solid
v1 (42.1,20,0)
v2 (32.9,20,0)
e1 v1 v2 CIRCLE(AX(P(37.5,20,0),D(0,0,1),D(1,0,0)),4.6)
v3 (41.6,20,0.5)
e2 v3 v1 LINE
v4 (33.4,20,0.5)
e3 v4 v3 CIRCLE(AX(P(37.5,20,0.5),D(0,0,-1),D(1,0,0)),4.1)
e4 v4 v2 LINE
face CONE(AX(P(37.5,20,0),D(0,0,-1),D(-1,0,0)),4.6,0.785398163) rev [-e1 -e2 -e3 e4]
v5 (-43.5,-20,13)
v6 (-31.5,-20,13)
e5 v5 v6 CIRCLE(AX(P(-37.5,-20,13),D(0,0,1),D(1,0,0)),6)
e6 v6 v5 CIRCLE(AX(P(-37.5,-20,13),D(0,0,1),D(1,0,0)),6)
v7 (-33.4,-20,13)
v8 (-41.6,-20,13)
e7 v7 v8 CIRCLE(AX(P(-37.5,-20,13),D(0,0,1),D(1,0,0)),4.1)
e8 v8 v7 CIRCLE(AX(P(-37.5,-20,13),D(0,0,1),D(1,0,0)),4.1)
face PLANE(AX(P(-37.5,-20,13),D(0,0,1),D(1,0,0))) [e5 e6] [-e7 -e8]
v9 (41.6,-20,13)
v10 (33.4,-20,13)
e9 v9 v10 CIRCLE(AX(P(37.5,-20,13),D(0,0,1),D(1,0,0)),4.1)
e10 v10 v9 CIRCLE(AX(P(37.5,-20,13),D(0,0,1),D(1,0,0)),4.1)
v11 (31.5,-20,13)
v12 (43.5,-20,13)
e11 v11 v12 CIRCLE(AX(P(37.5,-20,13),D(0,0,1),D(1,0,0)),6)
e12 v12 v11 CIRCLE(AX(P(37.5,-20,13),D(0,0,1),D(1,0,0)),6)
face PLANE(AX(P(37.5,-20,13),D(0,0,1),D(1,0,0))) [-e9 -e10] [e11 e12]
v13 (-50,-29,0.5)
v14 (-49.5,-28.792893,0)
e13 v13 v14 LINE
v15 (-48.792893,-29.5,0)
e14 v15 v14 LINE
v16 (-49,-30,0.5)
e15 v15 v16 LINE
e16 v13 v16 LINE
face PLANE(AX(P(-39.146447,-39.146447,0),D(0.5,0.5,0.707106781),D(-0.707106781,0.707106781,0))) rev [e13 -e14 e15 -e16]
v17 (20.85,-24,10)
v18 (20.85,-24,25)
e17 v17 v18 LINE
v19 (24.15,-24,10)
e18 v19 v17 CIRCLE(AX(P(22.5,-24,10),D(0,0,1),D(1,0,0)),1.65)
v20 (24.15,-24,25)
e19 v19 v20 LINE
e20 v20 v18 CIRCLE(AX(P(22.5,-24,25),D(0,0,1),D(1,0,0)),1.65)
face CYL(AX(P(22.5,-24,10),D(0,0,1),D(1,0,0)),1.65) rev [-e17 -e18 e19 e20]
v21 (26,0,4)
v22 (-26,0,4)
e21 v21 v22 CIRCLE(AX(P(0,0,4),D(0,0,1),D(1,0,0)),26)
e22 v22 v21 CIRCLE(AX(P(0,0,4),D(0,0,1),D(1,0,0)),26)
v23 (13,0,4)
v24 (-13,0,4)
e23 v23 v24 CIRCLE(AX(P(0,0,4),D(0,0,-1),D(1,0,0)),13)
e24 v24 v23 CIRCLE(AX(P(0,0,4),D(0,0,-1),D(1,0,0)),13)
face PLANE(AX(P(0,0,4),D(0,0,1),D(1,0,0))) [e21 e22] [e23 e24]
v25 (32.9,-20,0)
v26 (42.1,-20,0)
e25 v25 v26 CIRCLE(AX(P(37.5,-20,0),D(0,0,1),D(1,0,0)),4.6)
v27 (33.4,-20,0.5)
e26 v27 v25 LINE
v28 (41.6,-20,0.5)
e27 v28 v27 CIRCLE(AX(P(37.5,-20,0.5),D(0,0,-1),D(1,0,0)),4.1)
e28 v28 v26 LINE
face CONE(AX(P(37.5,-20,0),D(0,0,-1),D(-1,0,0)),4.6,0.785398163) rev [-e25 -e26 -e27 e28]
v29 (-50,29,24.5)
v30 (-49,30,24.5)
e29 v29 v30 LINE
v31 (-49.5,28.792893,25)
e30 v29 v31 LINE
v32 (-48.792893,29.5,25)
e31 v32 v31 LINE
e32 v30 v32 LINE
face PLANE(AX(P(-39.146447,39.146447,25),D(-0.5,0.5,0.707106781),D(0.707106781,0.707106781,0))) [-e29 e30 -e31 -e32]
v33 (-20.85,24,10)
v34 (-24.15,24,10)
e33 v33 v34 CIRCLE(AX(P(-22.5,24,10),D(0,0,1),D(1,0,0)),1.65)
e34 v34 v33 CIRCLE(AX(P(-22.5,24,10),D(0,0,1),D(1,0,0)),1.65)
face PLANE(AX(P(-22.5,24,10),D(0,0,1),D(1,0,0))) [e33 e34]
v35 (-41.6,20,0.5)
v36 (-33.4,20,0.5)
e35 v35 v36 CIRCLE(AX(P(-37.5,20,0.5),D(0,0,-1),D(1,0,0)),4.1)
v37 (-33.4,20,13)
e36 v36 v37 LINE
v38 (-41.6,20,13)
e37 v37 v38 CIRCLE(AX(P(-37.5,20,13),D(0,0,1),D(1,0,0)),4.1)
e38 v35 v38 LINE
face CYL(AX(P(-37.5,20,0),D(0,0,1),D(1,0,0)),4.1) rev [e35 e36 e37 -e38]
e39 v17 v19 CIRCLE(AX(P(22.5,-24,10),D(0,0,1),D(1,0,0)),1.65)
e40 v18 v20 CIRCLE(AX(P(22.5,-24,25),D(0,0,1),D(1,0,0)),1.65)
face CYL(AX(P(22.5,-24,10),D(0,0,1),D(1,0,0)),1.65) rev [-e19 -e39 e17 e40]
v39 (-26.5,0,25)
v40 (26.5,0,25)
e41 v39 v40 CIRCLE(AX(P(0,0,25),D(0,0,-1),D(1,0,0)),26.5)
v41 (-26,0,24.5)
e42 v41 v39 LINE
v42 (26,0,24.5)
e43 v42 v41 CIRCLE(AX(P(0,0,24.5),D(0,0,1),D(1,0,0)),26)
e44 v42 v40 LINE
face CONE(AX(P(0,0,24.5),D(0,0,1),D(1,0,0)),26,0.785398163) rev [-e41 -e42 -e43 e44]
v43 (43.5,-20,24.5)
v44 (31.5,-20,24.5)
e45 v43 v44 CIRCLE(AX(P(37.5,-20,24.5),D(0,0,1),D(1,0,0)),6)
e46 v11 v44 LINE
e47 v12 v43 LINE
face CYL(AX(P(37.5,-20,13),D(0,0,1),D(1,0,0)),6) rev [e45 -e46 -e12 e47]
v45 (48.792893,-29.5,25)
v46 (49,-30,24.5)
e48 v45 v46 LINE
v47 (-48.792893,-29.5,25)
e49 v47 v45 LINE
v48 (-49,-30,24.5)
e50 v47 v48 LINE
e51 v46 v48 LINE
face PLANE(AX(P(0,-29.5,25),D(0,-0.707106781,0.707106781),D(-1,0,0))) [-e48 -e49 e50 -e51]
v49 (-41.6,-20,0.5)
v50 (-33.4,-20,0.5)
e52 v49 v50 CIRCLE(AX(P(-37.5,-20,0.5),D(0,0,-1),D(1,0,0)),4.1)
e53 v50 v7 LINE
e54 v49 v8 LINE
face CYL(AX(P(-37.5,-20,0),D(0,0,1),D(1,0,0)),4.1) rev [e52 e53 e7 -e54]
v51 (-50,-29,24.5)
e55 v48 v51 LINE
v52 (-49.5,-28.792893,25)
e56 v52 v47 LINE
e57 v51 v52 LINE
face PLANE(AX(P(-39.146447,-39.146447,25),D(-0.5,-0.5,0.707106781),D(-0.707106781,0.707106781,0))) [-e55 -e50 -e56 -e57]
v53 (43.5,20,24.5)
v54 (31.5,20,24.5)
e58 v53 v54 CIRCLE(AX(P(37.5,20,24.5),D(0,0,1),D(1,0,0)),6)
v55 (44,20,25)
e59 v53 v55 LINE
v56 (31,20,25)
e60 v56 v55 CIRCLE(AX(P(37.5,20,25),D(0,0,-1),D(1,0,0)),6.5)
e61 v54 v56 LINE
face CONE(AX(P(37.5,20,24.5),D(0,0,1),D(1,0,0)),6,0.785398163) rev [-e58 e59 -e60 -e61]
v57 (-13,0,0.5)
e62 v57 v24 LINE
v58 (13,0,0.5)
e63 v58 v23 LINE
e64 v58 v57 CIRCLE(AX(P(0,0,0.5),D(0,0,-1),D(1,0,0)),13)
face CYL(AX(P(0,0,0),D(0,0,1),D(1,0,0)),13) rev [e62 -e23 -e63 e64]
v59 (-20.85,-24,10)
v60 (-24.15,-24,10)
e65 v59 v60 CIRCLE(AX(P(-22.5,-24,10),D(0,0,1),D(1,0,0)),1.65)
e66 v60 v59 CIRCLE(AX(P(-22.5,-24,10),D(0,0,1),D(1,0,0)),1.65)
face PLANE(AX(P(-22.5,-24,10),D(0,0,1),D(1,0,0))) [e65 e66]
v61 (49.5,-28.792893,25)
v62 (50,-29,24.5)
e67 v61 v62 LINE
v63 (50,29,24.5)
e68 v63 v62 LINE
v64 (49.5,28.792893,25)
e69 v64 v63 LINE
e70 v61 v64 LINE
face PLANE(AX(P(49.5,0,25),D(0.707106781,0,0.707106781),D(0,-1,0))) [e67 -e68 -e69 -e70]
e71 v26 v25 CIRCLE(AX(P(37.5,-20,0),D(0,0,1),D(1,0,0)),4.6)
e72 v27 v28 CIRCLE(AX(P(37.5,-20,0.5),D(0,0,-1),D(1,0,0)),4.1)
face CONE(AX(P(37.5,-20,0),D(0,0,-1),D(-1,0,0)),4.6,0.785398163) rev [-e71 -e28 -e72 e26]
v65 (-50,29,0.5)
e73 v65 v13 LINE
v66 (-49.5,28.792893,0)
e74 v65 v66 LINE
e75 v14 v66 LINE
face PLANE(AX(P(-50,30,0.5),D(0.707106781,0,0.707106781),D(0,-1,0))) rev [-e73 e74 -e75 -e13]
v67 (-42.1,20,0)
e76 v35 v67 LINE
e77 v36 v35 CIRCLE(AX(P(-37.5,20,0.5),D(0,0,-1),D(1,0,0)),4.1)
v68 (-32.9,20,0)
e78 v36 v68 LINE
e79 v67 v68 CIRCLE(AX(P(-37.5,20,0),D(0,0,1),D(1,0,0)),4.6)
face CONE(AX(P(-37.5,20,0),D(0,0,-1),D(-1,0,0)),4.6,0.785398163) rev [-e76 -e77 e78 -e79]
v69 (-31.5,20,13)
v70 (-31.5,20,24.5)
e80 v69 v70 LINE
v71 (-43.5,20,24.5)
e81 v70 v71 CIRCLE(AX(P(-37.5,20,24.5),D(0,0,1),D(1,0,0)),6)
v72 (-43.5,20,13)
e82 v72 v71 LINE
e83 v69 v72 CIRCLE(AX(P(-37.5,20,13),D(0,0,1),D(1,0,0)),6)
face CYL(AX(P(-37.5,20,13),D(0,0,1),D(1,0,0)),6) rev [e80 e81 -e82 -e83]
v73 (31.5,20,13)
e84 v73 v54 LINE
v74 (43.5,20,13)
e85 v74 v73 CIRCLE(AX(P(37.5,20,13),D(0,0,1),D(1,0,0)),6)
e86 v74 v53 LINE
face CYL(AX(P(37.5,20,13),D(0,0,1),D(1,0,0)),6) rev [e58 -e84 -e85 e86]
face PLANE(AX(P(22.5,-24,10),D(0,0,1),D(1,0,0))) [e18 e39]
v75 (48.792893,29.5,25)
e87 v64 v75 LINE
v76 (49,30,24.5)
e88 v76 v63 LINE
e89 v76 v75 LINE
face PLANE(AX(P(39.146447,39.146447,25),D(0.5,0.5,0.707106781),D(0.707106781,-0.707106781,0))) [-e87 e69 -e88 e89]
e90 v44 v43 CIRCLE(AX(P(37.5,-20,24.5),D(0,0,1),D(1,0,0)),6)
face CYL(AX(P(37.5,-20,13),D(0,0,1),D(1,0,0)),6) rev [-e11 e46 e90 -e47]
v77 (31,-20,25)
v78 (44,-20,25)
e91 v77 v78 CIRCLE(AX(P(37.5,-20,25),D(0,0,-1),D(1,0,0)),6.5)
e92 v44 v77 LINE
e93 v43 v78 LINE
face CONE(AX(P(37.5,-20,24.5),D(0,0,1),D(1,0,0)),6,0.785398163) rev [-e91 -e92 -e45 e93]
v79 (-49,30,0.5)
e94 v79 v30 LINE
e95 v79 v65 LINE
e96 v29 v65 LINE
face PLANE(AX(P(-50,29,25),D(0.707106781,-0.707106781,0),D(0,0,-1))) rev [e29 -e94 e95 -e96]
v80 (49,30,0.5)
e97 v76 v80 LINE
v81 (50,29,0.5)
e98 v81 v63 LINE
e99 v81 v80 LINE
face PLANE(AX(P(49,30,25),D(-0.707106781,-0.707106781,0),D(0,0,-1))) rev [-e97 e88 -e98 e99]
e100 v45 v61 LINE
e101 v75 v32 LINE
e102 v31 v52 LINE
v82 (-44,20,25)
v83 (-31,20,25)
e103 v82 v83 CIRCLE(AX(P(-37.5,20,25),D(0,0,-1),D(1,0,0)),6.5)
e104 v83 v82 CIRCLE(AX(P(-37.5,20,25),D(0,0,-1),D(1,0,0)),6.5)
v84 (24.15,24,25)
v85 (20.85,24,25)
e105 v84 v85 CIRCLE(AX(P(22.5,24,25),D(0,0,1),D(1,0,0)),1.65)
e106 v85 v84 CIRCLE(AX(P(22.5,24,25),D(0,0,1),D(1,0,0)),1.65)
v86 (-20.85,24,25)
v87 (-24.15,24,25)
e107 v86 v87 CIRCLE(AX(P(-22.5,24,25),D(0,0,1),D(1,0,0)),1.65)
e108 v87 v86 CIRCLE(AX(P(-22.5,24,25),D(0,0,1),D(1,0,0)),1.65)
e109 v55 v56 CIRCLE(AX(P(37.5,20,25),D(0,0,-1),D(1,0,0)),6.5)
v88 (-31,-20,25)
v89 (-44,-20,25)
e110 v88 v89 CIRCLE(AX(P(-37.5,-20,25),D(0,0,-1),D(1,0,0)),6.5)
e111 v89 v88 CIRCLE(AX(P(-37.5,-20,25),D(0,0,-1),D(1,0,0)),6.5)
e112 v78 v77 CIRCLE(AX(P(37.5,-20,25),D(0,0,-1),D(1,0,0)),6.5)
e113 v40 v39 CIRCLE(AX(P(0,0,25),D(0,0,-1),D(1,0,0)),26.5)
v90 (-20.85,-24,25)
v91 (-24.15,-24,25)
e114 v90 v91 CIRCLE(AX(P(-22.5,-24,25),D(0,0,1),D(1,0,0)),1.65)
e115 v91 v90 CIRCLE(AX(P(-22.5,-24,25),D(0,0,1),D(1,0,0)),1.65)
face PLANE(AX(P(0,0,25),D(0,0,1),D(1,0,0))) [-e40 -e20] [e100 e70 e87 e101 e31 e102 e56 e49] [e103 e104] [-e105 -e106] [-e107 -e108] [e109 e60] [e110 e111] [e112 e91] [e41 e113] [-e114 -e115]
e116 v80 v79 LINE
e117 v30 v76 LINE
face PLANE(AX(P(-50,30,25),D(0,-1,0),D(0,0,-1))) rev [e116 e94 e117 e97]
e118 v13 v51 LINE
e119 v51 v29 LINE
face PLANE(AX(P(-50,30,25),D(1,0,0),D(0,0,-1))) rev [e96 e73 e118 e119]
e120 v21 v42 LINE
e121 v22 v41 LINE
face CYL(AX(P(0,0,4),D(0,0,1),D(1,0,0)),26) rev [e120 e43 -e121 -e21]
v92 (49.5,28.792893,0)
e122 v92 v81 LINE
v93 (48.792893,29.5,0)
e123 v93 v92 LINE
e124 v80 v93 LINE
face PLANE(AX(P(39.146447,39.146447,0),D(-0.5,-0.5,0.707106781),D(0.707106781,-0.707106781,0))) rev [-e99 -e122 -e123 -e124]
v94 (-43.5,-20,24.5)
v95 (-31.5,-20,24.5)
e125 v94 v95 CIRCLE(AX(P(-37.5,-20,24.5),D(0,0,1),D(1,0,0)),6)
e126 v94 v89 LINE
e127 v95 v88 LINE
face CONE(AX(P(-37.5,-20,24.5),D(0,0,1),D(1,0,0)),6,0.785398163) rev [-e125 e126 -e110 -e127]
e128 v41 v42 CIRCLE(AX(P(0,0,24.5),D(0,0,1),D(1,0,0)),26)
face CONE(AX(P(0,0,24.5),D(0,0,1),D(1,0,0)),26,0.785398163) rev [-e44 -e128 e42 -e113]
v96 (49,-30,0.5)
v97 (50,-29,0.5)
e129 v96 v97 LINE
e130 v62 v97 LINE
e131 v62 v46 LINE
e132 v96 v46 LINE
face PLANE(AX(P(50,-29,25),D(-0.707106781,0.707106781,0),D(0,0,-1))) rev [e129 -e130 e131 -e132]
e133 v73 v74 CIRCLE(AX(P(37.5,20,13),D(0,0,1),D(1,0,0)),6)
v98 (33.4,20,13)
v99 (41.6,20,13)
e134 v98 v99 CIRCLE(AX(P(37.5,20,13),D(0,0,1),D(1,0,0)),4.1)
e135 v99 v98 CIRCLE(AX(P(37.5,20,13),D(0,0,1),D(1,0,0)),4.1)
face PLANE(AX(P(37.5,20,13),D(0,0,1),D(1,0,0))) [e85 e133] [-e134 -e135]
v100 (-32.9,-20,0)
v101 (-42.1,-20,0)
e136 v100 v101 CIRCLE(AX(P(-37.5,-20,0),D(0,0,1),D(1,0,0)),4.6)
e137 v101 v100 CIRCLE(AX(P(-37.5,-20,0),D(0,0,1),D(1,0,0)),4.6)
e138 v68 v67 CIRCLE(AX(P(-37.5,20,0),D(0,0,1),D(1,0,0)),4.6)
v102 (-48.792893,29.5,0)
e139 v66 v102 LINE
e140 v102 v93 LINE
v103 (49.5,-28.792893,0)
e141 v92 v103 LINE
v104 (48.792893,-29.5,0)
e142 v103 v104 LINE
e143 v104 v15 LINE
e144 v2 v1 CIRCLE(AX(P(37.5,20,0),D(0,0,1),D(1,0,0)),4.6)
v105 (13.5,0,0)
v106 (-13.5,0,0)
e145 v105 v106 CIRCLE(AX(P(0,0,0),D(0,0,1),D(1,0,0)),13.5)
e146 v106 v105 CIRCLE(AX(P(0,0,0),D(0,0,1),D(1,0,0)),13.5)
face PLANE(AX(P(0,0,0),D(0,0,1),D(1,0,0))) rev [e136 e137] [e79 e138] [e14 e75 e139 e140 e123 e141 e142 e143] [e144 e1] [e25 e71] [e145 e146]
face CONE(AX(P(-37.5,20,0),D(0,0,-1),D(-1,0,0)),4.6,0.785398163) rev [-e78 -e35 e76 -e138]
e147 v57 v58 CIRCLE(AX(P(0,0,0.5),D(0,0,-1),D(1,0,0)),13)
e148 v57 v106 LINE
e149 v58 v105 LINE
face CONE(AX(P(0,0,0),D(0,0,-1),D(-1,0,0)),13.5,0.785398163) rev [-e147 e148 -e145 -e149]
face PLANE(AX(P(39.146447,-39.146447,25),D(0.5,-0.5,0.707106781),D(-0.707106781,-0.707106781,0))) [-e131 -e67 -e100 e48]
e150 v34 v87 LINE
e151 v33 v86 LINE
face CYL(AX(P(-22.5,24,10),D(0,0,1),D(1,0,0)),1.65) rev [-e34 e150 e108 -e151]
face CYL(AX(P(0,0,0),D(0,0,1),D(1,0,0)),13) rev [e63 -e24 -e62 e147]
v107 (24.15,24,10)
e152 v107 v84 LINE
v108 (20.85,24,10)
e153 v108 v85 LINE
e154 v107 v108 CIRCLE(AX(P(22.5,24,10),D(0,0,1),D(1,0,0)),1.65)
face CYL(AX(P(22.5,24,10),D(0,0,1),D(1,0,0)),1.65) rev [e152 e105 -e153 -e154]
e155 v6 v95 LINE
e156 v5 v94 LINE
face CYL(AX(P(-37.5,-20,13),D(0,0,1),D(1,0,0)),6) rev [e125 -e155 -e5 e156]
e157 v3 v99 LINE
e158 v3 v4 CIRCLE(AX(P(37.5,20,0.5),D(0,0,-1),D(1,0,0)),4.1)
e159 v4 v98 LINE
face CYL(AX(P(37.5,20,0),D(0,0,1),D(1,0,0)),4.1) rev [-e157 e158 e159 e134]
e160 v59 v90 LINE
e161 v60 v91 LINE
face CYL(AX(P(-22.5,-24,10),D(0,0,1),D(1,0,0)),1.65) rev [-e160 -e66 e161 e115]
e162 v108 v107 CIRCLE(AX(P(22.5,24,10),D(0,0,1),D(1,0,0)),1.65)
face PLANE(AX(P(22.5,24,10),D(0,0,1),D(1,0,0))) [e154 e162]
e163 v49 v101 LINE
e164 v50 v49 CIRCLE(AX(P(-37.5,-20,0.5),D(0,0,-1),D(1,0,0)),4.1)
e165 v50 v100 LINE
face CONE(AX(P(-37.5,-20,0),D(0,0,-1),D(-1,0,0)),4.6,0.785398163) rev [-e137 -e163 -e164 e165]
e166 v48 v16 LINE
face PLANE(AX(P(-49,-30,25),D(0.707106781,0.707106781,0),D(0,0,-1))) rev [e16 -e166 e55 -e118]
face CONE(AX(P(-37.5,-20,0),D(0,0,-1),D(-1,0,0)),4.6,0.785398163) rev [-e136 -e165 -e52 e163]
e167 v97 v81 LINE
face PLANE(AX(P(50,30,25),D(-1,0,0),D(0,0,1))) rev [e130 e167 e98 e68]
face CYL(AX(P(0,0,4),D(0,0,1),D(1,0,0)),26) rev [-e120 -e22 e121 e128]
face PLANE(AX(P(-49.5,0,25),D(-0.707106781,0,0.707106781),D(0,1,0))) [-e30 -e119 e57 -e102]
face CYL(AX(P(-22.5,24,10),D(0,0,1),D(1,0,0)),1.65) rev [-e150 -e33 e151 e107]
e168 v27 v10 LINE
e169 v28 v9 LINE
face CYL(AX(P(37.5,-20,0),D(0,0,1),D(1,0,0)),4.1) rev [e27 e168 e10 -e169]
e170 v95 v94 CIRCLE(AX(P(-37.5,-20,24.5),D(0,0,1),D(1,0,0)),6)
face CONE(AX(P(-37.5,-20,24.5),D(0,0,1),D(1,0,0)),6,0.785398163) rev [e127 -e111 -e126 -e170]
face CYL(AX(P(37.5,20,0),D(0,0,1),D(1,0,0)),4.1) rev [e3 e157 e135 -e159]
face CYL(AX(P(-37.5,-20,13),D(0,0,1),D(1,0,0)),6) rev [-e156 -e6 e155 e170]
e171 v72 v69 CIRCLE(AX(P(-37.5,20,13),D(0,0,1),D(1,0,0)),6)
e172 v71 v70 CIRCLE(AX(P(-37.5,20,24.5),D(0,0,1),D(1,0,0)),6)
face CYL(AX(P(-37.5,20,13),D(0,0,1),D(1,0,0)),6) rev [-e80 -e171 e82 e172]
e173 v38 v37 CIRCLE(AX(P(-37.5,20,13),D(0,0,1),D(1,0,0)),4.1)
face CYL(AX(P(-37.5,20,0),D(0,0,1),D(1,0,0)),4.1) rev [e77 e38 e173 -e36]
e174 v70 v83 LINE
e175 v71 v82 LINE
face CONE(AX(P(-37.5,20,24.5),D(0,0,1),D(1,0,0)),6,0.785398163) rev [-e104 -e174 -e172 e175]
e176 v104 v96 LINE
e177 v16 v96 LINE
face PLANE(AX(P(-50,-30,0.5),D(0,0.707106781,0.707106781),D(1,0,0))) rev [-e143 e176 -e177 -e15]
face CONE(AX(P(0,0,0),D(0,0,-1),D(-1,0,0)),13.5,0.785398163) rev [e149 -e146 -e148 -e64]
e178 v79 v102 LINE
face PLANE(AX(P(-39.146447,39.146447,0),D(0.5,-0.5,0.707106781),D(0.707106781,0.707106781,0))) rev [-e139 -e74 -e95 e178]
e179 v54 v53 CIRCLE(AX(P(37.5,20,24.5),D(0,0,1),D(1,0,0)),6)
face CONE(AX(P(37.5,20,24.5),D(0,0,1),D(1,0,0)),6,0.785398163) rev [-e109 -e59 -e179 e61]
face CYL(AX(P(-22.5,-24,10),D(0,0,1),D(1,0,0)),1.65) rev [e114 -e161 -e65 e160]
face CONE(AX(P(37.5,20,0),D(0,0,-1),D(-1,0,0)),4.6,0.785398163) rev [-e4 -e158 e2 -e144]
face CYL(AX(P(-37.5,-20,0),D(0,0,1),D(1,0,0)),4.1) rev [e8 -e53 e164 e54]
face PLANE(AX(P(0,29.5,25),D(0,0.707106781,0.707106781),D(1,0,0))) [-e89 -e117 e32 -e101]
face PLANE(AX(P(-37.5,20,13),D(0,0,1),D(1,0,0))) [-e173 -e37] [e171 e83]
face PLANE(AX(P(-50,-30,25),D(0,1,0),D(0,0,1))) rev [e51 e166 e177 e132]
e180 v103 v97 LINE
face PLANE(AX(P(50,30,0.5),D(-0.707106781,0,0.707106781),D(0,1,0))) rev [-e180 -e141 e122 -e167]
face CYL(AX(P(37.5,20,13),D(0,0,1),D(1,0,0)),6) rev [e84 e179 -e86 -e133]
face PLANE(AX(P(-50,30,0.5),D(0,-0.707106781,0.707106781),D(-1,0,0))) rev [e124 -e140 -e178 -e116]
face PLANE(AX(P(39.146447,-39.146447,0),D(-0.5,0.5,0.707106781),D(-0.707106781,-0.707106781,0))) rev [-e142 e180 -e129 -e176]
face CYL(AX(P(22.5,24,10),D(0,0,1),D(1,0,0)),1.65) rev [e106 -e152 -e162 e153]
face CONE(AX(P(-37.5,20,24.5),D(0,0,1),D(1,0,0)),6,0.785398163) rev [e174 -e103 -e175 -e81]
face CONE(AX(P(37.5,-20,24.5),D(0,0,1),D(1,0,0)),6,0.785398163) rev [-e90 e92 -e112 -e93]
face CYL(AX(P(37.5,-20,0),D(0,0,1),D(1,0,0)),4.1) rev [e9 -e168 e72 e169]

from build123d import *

# Parameters (mm, degrees)
SKETCH_1_W          = 100
SKETCH_1_H          = 60
EXTRUDE_1_DEPTH     = 25
SKETCH_2_R          = 13
CUT_EXTRUDE_1_DEPTH = 64.442887702
SKETCH_3_R          = 6
CUT_EXTRUDE_2_DEPTH = 12
SKETCH_4_R          = 4.1
CUT_EXTRUDE_3_DEPTH = 64.442887702
CHAMFER_1_SIZE      = 1
CHAMFER_4_SIZE      = 0.5
SKETCH_8_R          = 26
CUT_EXTRUDE_5_DEPTH = 21
CHAMFER_5_SIZE      = 0.5
SKETCH_9_R          = 1.65
CUT_EXTRUDE_6_DEPTH = 15


with BuildPart() as part:
    # 草图1 → 凸台-拉伸1 (new body)
    with BuildSketch(Plane.XY):
        Rectangle(SKETCH_1_W, SKETCH_1_H)
    extrude(amount=EXTRUDE_1_DEPTH)

    # 草图2 → 切除-拉伸1 (cut, through all)
    with BuildSketch(Plane.XY.offset(25)):
        Circle(SKETCH_2_R)
    extrude(amount=-CUT_EXTRUDE_1_DEPTH, mode=Mode.SUBTRACT)

    # 草图3 → 切除-拉伸2 (cut)
    with BuildSketch(Plane.XY.offset(25)):
        with Locations((-37.5, 20)):
            Circle(SKETCH_3_R)
        with Locations((-37.5, -20)):
            Circle(SKETCH_3_R)
        with Locations((37.5, -20)):
            Circle(SKETCH_3_R)
        with Locations((37.5, 20)):
            Circle(SKETCH_3_R)
    extrude(amount=-CUT_EXTRUDE_2_DEPTH, mode=Mode.SUBTRACT)

    # 草图4 → 切除-拉伸3 (cut, through all)
    with BuildSketch(Plane.XY.offset(25)):
        with Locations((-37.5, 20)):
            Circle(SKETCH_4_R)
        with Locations((-37.5, -20)):
            Circle(SKETCH_4_R)
        with Locations((37.5, 20)):
            Circle(SKETCH_4_R)
        with Locations((37.5, -20)):
            Circle(SKETCH_4_R)
    extrude(amount=-CUT_EXTRUDE_3_DEPTH, mode=Mode.SUBTRACT)

    # 倒角1
    chamfer_1_edges = [part.edges().sort_by_distance(p)[0] for p in [
        (50, -30, 12.5),
        (-50, -30, 12.5),
        (-50, 30, 12.5),
        (50, 30, 12.5),
    ]]
    chamfer(chamfer_1_edges, length=CHAMFER_1_SIZE)

    # 倒角4
    chamfer_4_edges = [part.edges().sort_by_distance(p)[0] for p in [
        (-13, 0, 0),
        (-41.6, -20, 0),
        (33.4, 20, 0),
        (33.4, -20, 0),
        (-41.6, 20, 0),
        (-50, 0, 0),
        (50, 0, 0),
        (0, -30, 0),
        (0, 30, 0),
        (-49.5, -29.5, 0),
        (49.5, -29.5, 0),
        (49.5, 29.5, 0),
        (-49.5, 29.5, 0),
    ]]
    chamfer(chamfer_4_edges, length=CHAMFER_4_SIZE)

    # 草图8 → 切除-拉伸5 (cut)
    with BuildSketch(Plane.XY.offset(25)):
        Circle(SKETCH_8_R)
    extrude(amount=-CUT_EXTRUDE_5_DEPTH, mode=Mode.SUBTRACT)

    # 倒角5
    chamfer_5_edges = [part.edges().sort_by_distance(p)[0] for p in [
        (-26, 0, 25),
        (31.5, 20, 25),
        (31.5, -20, 25),
        (-43.5, -20, 25),
        (-43.5, 20, 25),
        (-50, 0, 25),
        (0, 30, 25),
        (50, 0, 25),
        (0, -30, 25),
        (-49.5, -29.5, 25),
        (49.5, -29.5, 25),
        (49.5, 29.5, 25),
        (-49.5, 29.5, 25),
    ]]
    chamfer(chamfer_5_edges, length=CHAMFER_5_SIZE)

    # 草图9 → 切除-拉伸6 (cut)
    with BuildSketch(Plane.XY.offset(25)):
        with Locations((22.5, -24)):
            Circle(SKETCH_9_R)
        with Locations((22.5, 24)):
            Circle(SKETCH_9_R)
        with Locations((-22.5, 24)):
            Circle(SKETCH_9_R)
        with Locations((-22.5, -24)):
            Circle(SKETCH_9_R)
    extrude(amount=-CUT_EXTRUDE_6_DEPTH, mode=Mode.SUBTRACT)


solid = part.part
